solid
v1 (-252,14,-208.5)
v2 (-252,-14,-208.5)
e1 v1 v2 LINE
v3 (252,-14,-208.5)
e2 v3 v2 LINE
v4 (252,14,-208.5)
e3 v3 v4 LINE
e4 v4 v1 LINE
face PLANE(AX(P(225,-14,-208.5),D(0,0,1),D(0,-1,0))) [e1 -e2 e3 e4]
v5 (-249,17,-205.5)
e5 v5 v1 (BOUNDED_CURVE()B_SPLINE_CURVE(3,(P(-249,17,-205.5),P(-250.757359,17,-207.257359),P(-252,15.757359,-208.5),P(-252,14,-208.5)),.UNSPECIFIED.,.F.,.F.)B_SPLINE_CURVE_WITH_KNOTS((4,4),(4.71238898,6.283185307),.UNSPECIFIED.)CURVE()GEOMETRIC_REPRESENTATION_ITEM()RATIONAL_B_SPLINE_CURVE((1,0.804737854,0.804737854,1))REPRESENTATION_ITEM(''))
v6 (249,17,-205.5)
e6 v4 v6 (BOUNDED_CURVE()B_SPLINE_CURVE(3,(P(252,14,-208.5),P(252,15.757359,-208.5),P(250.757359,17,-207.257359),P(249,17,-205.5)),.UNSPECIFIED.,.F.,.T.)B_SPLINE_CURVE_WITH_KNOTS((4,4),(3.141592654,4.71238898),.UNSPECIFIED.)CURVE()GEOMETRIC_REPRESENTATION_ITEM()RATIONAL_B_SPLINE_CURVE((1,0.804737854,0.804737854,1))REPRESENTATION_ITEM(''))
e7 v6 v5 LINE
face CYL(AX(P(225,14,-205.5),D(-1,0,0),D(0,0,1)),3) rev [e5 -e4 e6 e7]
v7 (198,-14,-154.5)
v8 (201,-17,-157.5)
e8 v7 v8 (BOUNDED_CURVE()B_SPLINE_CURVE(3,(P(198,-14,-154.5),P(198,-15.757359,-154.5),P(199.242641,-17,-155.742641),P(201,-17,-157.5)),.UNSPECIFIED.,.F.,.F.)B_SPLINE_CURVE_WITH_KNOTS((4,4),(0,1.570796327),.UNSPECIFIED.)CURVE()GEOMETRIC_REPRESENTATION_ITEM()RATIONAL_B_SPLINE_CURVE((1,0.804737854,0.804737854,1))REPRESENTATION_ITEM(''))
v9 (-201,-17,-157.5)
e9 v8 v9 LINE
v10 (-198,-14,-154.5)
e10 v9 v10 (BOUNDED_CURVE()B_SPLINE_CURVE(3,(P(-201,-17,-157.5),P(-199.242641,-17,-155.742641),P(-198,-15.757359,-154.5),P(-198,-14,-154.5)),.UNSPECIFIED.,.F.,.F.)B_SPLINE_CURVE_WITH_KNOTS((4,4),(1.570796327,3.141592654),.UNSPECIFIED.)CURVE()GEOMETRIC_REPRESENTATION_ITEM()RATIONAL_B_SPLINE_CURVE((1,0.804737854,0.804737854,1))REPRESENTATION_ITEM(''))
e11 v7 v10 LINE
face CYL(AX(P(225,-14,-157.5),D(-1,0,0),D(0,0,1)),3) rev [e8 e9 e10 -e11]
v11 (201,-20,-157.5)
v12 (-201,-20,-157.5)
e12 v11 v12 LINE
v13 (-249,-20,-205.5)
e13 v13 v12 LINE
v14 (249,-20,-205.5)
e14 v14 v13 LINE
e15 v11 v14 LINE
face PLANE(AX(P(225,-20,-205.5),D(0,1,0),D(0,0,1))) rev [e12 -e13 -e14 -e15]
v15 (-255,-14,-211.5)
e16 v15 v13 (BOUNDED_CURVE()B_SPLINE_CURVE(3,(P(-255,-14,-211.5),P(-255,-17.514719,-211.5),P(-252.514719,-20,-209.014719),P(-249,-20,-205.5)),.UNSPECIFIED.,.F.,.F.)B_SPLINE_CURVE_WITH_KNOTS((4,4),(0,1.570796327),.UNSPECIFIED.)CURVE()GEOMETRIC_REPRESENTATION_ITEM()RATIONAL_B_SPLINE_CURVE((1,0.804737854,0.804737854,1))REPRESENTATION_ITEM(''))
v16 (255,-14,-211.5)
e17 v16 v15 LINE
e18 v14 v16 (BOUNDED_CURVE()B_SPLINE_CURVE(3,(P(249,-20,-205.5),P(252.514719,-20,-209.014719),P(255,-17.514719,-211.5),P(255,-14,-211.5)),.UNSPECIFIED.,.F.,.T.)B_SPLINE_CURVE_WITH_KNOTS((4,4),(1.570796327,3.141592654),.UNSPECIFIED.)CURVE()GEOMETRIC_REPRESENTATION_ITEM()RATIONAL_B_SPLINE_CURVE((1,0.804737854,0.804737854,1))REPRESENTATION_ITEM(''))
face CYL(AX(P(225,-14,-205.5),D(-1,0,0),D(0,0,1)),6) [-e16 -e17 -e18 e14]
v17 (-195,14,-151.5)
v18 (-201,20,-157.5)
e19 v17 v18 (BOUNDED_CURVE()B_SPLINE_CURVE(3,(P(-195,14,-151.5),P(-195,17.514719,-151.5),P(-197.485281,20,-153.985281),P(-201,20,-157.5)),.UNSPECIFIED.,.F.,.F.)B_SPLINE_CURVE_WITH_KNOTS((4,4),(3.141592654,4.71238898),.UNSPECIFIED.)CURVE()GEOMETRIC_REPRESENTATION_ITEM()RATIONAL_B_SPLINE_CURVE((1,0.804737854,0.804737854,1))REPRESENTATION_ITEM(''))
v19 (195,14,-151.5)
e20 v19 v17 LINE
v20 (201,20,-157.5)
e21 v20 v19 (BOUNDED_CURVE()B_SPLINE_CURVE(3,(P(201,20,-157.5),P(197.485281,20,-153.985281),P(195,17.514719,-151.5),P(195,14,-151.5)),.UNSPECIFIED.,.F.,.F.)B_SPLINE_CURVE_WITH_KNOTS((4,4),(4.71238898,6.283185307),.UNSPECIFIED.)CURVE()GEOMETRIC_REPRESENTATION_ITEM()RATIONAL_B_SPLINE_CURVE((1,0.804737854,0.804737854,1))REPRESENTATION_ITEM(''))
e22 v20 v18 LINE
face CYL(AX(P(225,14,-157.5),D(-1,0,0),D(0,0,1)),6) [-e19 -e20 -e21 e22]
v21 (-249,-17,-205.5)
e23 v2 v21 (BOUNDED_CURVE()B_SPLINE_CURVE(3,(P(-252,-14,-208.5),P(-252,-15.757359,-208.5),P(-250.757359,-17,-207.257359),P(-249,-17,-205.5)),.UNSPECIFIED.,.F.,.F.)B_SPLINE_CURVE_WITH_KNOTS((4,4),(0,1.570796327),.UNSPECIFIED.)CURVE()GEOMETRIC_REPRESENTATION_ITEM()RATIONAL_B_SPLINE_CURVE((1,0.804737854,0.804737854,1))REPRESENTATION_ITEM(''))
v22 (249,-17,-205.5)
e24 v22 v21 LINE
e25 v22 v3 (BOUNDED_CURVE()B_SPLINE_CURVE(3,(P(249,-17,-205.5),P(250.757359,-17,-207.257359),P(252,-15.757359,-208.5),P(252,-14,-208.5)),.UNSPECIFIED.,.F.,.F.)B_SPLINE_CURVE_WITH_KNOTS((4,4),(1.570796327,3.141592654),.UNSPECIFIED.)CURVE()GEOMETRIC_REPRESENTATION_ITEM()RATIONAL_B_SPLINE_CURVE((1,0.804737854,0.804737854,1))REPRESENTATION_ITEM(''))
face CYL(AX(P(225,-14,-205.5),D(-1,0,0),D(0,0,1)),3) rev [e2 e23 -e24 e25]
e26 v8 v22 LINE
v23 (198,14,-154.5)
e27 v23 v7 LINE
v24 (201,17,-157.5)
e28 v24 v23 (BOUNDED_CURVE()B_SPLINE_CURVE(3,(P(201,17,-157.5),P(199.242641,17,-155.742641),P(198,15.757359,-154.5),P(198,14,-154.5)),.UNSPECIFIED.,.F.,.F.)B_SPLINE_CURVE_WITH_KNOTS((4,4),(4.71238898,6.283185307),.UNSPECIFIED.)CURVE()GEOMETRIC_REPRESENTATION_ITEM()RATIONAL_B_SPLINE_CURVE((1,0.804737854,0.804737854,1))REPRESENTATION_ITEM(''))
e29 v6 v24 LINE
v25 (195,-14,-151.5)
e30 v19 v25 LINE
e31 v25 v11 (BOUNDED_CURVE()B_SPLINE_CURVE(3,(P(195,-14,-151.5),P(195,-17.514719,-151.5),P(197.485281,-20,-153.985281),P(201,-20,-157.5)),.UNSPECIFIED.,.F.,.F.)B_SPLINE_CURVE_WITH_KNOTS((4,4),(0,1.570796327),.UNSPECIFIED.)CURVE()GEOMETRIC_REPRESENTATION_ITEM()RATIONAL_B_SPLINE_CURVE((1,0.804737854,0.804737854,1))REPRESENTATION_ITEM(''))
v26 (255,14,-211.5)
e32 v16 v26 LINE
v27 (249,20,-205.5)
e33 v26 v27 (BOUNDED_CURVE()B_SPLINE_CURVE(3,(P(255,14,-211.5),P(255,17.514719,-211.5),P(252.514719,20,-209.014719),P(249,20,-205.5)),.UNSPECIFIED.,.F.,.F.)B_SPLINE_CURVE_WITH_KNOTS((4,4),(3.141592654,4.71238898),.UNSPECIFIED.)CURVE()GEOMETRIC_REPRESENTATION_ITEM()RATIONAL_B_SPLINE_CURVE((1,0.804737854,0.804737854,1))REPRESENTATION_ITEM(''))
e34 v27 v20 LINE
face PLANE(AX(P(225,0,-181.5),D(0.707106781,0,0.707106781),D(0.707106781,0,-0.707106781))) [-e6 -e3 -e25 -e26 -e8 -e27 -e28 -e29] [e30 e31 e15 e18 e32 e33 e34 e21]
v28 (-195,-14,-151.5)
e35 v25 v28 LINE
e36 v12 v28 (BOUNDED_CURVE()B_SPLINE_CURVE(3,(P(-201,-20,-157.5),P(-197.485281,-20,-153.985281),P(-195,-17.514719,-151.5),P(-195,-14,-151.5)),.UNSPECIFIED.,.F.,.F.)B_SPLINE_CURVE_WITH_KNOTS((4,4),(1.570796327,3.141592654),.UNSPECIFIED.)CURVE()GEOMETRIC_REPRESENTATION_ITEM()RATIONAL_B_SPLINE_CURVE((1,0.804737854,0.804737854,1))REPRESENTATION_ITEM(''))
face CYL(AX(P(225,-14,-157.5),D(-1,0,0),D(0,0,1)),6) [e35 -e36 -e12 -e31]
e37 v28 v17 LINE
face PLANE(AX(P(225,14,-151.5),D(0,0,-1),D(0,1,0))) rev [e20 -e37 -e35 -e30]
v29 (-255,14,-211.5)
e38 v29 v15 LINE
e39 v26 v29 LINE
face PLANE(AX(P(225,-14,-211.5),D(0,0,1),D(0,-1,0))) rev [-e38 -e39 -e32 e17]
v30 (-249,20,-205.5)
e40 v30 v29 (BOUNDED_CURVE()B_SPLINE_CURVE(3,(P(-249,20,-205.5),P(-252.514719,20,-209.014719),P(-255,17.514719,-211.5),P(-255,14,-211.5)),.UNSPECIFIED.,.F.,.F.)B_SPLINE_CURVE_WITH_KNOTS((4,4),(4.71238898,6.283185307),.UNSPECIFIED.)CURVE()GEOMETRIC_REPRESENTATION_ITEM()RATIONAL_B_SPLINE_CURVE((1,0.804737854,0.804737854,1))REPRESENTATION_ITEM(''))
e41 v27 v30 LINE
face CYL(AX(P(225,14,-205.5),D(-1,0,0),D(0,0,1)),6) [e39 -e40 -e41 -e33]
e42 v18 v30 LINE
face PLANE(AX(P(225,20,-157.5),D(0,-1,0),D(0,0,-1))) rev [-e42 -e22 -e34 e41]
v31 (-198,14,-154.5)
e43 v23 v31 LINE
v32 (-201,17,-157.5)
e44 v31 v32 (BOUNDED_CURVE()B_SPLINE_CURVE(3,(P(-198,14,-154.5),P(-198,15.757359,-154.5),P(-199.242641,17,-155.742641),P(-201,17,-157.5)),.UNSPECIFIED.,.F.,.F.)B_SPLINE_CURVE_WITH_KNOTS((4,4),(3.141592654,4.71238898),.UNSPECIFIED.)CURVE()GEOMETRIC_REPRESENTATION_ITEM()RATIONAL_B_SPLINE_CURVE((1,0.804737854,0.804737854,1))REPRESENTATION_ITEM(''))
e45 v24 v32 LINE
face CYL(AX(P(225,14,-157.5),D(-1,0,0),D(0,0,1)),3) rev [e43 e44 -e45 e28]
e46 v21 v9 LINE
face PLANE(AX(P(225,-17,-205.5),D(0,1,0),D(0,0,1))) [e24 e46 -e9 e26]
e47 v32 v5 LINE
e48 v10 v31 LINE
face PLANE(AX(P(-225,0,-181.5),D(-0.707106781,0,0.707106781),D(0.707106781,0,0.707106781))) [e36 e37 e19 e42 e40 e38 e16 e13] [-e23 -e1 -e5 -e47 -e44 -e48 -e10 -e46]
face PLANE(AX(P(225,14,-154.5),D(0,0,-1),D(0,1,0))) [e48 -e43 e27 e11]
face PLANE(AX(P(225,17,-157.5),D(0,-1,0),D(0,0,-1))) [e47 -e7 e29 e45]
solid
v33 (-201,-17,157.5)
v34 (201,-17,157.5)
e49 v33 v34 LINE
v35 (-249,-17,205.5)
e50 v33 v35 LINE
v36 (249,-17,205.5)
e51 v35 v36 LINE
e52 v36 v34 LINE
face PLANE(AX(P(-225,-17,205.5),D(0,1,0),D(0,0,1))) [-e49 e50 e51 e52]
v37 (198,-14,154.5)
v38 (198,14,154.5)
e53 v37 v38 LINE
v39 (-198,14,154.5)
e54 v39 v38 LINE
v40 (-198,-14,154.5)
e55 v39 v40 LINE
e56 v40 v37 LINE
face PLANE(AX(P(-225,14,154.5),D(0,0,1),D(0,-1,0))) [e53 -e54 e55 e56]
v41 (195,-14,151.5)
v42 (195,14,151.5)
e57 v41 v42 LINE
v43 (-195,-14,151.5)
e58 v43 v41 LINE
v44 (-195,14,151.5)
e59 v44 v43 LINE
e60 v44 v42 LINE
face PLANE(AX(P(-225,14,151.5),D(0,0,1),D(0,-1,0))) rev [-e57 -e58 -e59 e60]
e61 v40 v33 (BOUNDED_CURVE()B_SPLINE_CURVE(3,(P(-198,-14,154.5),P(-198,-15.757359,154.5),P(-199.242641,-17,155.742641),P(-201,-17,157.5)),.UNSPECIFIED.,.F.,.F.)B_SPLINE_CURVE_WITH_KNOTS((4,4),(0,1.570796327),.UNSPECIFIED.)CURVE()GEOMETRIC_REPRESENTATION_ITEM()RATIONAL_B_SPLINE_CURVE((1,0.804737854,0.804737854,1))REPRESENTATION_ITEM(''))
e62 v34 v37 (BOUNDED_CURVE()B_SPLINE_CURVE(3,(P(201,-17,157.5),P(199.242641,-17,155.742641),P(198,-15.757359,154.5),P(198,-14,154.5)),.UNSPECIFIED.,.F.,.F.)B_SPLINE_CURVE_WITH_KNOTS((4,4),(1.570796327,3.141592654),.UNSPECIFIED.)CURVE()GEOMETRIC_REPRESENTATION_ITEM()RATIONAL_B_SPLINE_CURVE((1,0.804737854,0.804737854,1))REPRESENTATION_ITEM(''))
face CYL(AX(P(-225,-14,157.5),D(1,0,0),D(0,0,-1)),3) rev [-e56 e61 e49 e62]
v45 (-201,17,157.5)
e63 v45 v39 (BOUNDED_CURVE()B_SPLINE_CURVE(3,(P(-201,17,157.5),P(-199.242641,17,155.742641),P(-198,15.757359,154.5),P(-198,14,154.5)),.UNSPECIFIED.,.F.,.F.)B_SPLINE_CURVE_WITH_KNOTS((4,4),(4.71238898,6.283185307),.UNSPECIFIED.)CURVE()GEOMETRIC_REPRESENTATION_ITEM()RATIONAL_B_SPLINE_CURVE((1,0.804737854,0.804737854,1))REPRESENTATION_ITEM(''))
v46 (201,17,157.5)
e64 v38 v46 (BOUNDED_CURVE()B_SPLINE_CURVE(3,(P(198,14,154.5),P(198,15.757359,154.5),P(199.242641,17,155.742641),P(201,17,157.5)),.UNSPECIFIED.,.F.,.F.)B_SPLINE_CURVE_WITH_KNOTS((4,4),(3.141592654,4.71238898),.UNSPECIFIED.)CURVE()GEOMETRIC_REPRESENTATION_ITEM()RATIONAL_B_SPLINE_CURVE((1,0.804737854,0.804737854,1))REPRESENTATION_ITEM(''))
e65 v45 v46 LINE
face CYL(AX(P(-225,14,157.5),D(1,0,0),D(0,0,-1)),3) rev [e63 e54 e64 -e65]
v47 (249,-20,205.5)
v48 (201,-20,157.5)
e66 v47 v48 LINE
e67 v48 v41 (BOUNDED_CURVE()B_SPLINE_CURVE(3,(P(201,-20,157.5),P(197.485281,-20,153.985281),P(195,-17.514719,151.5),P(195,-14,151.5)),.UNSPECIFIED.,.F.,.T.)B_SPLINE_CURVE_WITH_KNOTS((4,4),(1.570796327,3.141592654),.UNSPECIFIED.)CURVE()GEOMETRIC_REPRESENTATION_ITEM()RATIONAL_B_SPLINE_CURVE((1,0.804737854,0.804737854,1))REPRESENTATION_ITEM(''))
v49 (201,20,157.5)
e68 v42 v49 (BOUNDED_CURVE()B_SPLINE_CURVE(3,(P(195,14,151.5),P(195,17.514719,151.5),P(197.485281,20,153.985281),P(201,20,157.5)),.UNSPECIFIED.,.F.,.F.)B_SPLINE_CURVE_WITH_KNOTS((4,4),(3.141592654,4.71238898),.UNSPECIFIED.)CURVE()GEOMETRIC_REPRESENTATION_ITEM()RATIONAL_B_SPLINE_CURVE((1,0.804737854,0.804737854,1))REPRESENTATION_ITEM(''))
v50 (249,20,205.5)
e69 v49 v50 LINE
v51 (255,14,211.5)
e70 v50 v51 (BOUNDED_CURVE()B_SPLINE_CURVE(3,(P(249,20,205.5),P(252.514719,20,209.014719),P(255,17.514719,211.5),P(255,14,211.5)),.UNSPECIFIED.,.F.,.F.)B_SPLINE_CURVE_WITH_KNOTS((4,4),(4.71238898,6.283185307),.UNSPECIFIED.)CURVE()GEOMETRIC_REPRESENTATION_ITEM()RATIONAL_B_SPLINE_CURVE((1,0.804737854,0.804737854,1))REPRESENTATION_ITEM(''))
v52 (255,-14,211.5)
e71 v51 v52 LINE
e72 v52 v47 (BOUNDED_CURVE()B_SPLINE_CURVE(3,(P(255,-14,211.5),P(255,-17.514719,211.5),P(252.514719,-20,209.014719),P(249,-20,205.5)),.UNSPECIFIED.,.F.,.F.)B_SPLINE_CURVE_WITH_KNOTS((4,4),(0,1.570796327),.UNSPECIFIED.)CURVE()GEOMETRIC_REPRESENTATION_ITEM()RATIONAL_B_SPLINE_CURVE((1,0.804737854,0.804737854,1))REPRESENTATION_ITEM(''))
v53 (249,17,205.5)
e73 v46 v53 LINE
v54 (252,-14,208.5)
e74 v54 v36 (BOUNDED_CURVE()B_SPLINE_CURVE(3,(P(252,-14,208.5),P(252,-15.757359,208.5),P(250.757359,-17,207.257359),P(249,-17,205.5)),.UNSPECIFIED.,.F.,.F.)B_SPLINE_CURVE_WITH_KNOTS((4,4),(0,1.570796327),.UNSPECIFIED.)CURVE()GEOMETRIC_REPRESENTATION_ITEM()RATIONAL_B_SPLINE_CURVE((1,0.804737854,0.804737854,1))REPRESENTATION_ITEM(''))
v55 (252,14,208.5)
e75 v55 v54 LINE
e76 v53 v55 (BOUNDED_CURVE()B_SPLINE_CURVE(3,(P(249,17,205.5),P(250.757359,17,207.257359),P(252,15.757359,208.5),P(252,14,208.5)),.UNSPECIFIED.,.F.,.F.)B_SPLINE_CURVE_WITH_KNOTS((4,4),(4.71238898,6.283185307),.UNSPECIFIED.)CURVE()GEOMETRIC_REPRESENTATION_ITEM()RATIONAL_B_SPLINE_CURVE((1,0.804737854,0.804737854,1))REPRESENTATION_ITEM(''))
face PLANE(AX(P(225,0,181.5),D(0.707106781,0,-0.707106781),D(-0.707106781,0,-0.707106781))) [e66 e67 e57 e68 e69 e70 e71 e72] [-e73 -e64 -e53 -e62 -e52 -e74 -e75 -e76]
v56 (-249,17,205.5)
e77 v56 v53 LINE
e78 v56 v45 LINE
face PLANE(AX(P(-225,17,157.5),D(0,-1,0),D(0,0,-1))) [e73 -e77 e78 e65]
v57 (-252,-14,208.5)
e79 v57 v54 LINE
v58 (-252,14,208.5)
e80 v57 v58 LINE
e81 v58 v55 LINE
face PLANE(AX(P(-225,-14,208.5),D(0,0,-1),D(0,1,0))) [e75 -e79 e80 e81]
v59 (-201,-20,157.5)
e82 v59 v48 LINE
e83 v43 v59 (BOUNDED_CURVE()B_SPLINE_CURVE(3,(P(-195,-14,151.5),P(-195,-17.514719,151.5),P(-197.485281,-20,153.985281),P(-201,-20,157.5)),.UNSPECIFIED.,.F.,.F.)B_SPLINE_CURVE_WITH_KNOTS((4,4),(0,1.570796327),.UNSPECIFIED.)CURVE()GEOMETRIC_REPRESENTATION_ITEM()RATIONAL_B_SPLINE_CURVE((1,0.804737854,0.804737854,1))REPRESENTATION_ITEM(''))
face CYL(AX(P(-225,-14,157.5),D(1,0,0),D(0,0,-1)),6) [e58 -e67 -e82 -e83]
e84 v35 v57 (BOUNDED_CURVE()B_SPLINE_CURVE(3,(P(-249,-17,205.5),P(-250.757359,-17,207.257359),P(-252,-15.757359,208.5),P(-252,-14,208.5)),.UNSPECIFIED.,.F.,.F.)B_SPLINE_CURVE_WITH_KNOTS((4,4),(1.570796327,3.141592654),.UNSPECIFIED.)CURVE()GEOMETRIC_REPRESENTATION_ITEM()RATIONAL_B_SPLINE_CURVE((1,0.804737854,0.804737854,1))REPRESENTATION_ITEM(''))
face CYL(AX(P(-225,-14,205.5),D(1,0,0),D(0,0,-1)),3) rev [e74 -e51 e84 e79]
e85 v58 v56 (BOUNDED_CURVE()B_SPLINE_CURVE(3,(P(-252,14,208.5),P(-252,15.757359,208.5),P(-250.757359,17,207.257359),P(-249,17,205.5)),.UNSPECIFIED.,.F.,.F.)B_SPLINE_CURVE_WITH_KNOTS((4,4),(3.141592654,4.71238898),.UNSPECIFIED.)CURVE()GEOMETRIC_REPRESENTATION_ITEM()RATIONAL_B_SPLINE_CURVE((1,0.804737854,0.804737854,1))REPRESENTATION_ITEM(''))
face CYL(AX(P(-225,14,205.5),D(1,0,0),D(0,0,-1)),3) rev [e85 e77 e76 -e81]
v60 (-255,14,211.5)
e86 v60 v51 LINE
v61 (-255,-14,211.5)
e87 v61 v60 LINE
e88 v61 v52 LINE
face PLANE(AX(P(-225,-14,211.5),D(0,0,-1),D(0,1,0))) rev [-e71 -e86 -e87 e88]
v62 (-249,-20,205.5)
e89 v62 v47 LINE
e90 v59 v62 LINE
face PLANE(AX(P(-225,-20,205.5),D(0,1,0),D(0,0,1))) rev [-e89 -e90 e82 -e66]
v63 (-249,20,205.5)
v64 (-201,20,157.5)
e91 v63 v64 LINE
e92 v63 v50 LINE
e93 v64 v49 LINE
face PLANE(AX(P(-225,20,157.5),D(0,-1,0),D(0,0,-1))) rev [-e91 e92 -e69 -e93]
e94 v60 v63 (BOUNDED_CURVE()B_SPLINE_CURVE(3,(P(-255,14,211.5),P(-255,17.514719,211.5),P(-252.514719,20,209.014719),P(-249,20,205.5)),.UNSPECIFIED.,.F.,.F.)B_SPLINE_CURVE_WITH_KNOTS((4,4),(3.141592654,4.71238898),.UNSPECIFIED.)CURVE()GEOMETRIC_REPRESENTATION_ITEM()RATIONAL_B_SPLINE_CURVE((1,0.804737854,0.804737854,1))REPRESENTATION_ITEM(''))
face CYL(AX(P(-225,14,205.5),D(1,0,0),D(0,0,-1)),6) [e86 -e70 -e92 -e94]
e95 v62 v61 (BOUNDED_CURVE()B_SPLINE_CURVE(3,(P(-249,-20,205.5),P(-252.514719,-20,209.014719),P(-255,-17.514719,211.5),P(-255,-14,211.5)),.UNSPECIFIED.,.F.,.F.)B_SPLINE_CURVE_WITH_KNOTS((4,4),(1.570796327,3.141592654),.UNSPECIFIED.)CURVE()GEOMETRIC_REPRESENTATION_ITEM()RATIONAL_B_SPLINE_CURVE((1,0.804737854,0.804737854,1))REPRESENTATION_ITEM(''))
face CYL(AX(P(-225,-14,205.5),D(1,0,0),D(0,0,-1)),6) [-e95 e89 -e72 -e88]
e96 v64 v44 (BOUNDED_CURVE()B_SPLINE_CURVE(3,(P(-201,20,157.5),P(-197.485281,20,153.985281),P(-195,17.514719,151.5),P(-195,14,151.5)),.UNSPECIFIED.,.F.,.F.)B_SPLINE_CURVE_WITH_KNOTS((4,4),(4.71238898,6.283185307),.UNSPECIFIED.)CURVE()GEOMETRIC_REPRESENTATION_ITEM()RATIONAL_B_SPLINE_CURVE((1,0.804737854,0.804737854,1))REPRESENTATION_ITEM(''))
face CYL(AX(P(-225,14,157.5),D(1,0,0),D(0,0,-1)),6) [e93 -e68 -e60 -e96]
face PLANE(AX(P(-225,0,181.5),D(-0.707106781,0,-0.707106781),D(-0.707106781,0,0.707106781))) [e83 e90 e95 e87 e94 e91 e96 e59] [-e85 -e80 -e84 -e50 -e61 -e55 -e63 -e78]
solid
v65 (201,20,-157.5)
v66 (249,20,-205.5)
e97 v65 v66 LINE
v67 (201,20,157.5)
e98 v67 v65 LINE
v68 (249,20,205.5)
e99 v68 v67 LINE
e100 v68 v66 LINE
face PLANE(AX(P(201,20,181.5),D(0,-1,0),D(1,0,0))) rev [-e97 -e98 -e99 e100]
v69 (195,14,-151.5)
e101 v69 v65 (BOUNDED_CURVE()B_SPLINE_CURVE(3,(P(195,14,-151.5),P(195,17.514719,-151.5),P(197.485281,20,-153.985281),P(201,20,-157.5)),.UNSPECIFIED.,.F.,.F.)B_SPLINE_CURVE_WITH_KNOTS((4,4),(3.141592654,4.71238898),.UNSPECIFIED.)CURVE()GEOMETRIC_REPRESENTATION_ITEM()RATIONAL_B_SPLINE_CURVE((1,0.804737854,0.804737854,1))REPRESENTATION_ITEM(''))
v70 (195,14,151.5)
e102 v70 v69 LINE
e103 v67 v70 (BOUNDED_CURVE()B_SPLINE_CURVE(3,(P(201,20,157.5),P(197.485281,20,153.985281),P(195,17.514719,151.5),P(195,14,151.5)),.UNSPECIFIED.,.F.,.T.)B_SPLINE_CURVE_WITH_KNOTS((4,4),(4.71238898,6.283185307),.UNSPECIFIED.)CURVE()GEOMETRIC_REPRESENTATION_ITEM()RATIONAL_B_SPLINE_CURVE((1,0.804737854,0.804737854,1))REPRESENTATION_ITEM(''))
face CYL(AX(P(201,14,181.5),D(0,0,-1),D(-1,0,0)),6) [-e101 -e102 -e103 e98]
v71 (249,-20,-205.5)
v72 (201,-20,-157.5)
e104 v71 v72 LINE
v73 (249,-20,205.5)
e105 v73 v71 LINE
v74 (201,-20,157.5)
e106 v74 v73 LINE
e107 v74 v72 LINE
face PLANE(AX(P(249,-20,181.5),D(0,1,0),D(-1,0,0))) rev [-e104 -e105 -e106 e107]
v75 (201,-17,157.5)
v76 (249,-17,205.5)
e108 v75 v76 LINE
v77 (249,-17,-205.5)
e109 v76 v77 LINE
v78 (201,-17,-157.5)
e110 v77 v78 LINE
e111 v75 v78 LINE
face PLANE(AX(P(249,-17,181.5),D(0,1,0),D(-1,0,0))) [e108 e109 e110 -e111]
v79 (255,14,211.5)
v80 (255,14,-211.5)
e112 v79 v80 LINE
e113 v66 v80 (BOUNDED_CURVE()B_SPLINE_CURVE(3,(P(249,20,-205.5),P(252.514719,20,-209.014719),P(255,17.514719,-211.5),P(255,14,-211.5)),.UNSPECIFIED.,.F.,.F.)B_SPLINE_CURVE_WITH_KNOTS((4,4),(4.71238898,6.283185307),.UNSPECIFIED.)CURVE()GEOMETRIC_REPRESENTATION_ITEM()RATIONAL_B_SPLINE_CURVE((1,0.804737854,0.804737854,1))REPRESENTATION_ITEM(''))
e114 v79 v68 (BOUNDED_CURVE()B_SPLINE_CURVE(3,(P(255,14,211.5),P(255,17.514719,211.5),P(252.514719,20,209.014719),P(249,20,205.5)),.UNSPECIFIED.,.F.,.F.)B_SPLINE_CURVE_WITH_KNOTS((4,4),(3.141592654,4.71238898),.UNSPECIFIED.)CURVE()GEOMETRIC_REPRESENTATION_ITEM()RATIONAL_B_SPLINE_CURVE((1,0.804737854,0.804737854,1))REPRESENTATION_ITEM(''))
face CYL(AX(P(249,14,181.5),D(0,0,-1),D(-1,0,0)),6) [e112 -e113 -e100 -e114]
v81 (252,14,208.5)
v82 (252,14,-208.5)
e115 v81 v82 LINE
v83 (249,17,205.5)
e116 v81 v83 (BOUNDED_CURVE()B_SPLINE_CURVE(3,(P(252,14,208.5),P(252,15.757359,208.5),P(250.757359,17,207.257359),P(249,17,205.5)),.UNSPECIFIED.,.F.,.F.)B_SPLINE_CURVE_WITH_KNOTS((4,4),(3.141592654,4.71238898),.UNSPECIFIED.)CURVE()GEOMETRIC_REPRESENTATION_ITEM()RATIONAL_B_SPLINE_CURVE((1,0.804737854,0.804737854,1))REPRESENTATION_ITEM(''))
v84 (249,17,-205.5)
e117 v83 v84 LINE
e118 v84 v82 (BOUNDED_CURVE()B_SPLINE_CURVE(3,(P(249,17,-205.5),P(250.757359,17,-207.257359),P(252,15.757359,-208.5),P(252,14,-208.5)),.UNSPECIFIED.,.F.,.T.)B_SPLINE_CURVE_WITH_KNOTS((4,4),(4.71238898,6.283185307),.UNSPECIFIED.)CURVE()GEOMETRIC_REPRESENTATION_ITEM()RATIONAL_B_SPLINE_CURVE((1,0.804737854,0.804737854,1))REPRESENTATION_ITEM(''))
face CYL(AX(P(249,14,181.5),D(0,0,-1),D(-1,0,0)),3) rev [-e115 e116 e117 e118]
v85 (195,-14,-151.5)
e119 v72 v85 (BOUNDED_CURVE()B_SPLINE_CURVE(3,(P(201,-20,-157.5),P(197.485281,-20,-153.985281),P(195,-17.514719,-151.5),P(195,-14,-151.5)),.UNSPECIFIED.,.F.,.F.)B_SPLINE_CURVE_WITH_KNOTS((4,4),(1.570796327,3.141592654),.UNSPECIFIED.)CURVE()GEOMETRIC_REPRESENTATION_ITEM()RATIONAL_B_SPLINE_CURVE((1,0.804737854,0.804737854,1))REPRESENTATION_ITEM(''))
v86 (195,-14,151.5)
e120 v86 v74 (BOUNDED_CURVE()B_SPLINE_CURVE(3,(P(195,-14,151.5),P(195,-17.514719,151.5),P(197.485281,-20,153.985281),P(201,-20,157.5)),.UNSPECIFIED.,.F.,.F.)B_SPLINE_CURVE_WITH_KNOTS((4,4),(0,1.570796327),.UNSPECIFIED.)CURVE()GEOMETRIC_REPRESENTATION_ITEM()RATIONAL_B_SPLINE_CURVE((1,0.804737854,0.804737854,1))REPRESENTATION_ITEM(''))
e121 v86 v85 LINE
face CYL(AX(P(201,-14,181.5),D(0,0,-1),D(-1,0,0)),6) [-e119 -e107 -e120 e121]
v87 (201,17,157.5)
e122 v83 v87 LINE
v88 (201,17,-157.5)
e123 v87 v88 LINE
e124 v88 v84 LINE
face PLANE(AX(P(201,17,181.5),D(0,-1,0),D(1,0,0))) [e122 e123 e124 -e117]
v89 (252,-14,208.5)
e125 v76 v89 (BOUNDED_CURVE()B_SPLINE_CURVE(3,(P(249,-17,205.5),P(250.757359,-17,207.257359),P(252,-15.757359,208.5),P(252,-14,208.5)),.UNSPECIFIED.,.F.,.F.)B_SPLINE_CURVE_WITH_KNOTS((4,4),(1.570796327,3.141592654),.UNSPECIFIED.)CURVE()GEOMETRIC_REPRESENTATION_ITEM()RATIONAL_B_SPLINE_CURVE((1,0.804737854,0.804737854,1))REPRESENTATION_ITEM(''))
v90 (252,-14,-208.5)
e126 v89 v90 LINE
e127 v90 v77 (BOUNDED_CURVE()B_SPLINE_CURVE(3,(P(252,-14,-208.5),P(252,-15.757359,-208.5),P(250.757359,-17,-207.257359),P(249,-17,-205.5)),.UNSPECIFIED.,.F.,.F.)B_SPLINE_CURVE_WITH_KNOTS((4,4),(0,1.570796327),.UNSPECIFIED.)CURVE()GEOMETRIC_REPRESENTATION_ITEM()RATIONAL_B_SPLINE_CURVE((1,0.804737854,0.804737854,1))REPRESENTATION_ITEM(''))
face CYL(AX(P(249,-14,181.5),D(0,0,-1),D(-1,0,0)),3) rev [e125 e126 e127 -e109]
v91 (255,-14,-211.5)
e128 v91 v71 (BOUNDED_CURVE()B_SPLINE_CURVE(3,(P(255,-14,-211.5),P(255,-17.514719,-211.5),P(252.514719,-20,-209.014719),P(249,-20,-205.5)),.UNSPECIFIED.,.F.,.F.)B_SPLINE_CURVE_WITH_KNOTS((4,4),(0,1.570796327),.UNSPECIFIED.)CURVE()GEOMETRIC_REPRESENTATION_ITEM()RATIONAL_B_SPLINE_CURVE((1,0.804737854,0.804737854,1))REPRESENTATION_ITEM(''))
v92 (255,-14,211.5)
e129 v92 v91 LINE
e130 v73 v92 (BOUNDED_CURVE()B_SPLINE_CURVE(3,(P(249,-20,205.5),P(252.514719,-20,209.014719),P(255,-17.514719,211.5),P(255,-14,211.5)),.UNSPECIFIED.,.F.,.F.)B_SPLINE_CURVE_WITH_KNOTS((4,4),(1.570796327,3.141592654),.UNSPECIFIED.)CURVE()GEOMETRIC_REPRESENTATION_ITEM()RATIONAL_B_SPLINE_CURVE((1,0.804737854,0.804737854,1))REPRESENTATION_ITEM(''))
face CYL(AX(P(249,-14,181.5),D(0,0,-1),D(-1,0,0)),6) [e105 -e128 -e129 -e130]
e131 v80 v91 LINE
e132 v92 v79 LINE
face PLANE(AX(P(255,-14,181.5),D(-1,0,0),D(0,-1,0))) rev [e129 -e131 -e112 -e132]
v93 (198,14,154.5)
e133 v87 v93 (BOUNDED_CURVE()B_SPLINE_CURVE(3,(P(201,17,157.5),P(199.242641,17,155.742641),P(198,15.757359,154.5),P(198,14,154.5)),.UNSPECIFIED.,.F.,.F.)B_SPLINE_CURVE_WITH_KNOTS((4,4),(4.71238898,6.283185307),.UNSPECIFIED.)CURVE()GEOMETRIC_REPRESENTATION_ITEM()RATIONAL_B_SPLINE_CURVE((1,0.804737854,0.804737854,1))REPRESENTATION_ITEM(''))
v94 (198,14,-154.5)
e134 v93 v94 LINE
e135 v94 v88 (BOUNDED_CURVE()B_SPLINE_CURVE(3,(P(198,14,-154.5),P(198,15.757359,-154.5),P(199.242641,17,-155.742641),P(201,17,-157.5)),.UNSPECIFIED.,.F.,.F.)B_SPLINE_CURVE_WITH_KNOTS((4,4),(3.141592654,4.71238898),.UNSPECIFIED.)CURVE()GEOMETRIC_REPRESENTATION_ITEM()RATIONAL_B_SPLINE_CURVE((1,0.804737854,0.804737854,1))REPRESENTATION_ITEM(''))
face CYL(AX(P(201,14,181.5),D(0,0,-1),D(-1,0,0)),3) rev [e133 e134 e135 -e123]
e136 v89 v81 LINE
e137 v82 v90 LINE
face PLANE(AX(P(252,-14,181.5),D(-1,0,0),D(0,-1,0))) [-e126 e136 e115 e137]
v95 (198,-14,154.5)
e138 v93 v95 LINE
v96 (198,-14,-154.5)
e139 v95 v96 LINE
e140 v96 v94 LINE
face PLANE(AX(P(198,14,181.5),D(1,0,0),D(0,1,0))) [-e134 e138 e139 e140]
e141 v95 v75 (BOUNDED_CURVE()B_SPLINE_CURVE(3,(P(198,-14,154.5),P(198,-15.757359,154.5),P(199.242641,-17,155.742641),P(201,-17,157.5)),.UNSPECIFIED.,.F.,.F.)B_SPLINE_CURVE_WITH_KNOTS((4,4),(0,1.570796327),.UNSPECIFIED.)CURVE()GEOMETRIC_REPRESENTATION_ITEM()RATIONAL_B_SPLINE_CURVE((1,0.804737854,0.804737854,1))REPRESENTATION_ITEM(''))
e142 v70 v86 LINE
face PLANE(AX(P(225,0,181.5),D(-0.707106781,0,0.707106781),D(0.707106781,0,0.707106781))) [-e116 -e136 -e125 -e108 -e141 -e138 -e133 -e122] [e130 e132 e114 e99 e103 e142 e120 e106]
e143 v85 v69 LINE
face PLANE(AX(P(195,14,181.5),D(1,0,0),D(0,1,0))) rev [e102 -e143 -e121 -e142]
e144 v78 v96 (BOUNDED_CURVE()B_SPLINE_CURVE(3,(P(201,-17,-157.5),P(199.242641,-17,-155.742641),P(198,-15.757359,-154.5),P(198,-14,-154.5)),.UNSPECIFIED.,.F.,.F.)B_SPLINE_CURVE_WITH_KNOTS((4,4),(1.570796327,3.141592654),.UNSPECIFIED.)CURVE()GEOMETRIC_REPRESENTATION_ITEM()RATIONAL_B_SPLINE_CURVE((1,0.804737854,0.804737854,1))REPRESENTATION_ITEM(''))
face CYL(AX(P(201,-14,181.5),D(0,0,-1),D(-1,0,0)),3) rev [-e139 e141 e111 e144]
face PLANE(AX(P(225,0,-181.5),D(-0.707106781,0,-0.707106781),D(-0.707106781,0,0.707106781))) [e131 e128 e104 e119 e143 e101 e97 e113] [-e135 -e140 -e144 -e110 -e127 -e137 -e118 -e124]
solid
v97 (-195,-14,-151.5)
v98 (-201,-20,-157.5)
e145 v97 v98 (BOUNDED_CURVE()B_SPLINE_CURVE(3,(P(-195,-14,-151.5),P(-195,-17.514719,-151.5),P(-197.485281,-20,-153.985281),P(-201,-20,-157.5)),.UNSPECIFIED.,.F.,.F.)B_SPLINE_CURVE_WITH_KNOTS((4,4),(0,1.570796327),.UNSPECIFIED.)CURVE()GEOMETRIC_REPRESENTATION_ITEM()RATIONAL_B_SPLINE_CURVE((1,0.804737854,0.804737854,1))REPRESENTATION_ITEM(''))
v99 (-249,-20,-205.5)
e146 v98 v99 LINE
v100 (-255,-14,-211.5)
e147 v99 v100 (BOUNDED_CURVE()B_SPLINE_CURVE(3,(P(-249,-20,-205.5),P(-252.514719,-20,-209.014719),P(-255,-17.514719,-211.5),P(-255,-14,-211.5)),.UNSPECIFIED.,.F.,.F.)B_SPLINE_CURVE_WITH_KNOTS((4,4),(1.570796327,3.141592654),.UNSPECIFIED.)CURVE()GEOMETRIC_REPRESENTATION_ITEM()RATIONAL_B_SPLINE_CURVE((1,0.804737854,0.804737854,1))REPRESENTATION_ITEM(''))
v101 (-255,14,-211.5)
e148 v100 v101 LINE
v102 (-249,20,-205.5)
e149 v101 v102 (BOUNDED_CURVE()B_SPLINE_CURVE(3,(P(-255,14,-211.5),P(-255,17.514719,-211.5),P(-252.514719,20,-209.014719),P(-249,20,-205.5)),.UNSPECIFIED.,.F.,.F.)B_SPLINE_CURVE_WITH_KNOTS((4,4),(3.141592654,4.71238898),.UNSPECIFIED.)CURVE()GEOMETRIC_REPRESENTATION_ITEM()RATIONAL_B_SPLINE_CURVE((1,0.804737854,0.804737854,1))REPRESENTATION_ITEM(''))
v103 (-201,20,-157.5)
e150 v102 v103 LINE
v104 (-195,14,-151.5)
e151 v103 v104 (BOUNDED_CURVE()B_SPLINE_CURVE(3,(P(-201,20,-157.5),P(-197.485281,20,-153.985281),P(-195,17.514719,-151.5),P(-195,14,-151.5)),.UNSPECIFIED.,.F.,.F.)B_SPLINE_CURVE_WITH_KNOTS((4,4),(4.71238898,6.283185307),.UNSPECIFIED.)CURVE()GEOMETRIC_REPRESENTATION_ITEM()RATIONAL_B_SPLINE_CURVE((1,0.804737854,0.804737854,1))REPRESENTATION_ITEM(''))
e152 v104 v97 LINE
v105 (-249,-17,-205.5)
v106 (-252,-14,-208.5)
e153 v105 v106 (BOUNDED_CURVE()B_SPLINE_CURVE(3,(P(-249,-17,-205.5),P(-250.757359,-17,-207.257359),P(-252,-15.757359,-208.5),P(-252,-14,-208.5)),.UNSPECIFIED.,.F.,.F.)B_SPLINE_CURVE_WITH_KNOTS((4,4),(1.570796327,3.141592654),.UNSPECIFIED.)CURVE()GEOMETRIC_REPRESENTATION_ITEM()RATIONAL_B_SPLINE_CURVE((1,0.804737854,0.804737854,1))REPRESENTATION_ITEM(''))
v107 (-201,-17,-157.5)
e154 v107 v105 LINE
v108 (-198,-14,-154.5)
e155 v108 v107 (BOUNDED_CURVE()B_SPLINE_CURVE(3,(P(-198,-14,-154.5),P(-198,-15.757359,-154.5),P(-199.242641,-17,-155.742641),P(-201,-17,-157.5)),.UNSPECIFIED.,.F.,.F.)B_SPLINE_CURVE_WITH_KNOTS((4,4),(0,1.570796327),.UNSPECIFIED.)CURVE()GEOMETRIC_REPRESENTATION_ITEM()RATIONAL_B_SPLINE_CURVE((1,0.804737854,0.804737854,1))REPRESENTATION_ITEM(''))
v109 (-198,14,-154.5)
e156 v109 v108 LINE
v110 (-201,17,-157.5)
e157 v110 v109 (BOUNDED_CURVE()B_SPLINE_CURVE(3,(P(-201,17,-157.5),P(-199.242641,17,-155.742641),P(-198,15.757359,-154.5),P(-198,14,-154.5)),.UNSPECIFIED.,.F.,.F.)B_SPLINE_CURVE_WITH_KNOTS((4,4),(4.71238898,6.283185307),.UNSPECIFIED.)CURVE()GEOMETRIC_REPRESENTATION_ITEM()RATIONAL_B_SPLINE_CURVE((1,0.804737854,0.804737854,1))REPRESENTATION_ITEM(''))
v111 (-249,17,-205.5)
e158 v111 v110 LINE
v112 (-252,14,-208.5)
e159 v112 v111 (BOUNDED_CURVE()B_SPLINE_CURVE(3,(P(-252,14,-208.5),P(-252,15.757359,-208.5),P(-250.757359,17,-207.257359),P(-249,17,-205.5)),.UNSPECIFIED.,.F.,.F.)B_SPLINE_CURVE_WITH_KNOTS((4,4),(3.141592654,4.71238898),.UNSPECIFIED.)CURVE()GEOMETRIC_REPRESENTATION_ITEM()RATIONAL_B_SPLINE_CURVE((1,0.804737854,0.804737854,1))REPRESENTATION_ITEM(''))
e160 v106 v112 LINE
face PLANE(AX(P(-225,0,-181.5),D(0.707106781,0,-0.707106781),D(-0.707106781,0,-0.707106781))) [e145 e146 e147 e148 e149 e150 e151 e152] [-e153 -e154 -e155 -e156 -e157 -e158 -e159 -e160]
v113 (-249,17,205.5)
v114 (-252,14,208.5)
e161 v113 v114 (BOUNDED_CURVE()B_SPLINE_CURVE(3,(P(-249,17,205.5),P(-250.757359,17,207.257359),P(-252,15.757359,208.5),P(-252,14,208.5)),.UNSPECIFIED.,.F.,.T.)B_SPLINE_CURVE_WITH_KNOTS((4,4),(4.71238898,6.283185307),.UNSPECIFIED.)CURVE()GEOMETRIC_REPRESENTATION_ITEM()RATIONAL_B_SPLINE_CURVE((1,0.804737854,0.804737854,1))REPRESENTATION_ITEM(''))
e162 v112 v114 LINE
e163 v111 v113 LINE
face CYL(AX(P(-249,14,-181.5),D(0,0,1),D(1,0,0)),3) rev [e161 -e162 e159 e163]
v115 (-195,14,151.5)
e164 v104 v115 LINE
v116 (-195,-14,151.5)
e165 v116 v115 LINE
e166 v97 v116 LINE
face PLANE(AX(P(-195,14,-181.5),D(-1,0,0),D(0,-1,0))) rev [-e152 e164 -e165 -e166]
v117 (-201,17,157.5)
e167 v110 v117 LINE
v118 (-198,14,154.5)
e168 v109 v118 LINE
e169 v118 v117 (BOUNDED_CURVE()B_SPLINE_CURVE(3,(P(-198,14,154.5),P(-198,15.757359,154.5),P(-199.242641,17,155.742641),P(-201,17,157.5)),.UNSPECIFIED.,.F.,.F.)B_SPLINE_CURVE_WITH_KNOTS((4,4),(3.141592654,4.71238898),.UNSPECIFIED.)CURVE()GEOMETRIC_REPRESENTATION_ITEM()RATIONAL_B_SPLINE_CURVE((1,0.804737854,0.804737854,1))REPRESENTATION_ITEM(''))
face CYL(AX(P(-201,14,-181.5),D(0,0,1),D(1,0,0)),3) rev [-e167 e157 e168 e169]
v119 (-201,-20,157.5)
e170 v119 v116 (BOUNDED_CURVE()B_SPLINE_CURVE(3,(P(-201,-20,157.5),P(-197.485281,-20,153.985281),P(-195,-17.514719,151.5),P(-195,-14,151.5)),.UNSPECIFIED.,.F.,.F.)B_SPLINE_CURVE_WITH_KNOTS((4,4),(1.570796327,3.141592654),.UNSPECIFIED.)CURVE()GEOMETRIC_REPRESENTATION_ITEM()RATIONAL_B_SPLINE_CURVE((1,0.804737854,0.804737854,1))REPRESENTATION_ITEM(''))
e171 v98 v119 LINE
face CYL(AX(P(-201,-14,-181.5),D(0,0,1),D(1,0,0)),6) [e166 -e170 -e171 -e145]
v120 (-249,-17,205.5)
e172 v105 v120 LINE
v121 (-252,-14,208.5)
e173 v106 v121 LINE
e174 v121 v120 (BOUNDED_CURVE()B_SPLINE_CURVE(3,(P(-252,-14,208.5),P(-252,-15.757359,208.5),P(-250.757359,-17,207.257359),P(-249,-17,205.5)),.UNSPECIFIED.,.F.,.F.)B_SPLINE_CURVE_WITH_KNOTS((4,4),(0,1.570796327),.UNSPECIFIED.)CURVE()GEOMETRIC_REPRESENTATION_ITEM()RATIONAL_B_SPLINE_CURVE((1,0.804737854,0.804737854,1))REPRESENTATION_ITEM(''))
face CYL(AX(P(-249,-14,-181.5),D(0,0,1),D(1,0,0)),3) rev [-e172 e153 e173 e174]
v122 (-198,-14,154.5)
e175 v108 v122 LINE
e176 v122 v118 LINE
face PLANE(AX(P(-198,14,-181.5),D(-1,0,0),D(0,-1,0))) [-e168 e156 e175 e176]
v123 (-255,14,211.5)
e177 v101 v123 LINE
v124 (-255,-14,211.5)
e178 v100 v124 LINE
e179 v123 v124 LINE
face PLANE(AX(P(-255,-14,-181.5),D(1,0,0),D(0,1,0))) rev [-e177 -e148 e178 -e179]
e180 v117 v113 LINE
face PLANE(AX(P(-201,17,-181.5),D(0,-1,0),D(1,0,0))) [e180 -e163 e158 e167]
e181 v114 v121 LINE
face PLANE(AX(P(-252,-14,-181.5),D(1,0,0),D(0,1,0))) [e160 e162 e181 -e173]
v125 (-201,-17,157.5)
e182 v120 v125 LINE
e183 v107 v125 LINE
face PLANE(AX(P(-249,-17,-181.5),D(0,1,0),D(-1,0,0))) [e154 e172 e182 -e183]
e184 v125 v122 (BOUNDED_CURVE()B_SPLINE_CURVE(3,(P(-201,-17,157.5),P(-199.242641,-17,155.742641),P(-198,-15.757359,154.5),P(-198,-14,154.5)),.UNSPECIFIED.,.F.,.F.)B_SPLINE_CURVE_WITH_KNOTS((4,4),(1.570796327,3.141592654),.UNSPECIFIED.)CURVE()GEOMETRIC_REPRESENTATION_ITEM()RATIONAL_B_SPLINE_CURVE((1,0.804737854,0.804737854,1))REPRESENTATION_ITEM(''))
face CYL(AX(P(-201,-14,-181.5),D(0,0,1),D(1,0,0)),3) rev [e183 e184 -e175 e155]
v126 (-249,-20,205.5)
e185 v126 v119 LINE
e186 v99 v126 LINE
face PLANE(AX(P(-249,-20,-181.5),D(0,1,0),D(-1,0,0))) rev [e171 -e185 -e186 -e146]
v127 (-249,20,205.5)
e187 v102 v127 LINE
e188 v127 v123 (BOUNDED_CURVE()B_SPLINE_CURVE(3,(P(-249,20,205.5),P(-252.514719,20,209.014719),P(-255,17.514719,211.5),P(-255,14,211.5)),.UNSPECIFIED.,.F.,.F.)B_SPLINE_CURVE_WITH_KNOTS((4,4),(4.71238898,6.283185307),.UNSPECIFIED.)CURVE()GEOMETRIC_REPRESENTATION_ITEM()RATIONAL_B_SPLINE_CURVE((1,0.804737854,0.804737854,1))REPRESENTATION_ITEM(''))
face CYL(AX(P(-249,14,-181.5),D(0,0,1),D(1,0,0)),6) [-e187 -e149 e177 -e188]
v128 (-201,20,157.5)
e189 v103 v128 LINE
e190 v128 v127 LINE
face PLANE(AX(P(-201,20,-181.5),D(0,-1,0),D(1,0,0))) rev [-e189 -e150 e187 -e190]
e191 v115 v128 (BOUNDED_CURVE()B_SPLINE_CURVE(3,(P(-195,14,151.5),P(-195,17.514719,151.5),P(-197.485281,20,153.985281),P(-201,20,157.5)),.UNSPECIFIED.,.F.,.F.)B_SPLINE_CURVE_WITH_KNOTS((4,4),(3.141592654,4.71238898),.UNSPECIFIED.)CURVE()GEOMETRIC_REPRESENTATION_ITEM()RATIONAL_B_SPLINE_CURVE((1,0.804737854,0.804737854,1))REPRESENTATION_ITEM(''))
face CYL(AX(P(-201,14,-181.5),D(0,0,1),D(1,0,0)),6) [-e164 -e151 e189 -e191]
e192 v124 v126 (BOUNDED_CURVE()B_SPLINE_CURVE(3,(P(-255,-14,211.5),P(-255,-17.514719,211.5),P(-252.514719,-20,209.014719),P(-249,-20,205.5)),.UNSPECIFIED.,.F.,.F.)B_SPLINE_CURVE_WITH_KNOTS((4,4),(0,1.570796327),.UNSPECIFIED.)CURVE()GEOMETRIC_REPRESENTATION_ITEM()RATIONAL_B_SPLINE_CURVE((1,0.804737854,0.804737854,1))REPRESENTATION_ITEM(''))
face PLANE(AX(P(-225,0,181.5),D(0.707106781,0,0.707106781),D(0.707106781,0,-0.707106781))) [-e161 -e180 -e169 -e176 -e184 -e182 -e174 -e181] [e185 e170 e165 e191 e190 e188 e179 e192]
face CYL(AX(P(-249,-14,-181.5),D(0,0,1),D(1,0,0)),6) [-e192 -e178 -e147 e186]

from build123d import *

# Parameters (mm, degrees)
GB_T_6728_2002_RECTANGULAR_HOLLOW_SECTIO_DEPTH      = 400.055512755
GB_T_6728_2002_RECTANGULAR_HOLLOW_SECTIO_DEPTH_BACK = 37.055512755
GB_T_6728_2002_RECTANGULAR_HOLLOW_SE_4_DEPTH        = 524.111025509
GB_T_6728_2002_RECTANGULAR_HOLLOW_SE_6_DEPTH        = 437.111025509
GB_T_6728_2002_RECTANGULAR_HOLLOW_SE_8_DEPTH        = 524.111025509


with BuildPart() as part:
    # Sketch1 → GB/T 6728-2002 Rectangular Hollow Section 60X40X3(1) (new, two sides: drawn at the far end of the back side and taken through both)
    with BuildSketch(Plane(origin=(-225, 0, 181.5), x_dir=(0, 1, 0), z_dir=(0, 0, -1)).offset(-GB_T_6728_2002_RECTANGULAR_HOLLOW_SECTIO_DEPTH_BACK)):
        with BuildLine():
            Line((-14, -30), (14, -30))
            ThreePointArc((14, -30), (18.242640687, -28.242640687), (20, -24))
            Line((20, -24), (20, 24))
            ThreePointArc((20, 24), (18.242640687, 28.242640687), (14, 30))
            Line((14, 30), (-14, 30))
            ThreePointArc((-14, 30), (-18.242640687, 28.242640687), (-20, 24))
            Line((-20, 24), (-20, -24))
            ThreePointArc((-20, -24), (-18.242640687, -28.242640687), (-14, -30))
        make_face()
        with BuildLine():
            Line((-14, -27), (14, -27))
            ThreePointArc((14, -27), (16.121320344, -26.121320344), (17, -24))
            Line((17, -24), (17, 24))
            ThreePointArc((17, 24), (16.121320344, 26.121320344), (14, 27))
            Line((14, 27), (-14, 27))
            ThreePointArc((-14, 27), (-16.121320344, 26.121320344), (-17, 24))
            Line((-17, 24), (-17, -24))
            ThreePointArc((-17, -24), (-16.121320344, -26.121320344), (-14, -27))
        make_face(mode=Mode.SUBTRACT)
    extrude(amount=GB_T_6728_2002_RECTANGULAR_HOLLOW_SECTIO_DEPTH + GB_T_6728_2002_RECTANGULAR_HOLLOW_SECTIO_DEPTH_BACK)

    # GB_T 6728-2002 Rectangular Hollow Se 2
    split(bisect_by=Plane(origin=(-225, 0, 181.5), x_dir=(0, -1, 0), z_dir=(-0.707106781, 0, -0.707106781)), keep=Keep.TOP)

    # GB_T 6728-2002 Rectangular Hollow Se 3
    split(bisect_by=Plane(origin=(-225, 0, -181.5), x_dir=(0, -1, 0), z_dir=(-0.707106781, 0, 0.707106781)), keep=Keep.TOP)


with BuildPart() as body_2:
    # Sketch1 on segment 2 (carried to segment 2) → GB_T 6728-2002 Rectangular Hollow Se 4 (new body)
    with BuildSketch(Plane(origin=(-262.055512755, 0, -181.5), x_dir=(0, 1, 0), z_dir=(1, 0, 0))):
        with BuildLine():
            Line((-14, -30), (14, -30))
            ThreePointArc((14, -30), (18.242640687, -28.242640687), (20, -24))
            Line((20, -24), (20, 24))
            ThreePointArc((20, 24), (18.242640687, 28.242640687), (14, 30))
            Line((14, 30), (-14, 30))
            ThreePointArc((-14, 30), (-18.242640687, 28.242640687), (-20, 24))
            Line((-20, 24), (-20, -24))
            ThreePointArc((-20, -24), (-18.242640687, -28.242640687), (-14, -30))
        make_face()
        with BuildLine():
            Line((-14, -27), (14, -27))
            ThreePointArc((14, -27), (16.121320344, -26.121320344), (17, -24))
            Line((17, -24), (17, 24))
            ThreePointArc((17, 24), (16.121320344, 26.121320344), (14, 27))
            Line((14, 27), (-14, 27))
            ThreePointArc((-14, 27), (-16.121320344, 26.121320344), (-17, 24))
            Line((-17, 24), (-17, -24))
            ThreePointArc((-17, -24), (-16.121320344, -26.121320344), (-14, -27))
        make_face(mode=Mode.SUBTRACT)
    extrude(amount=GB_T_6728_2002_RECTANGULAR_HOLLOW_SE_4_DEPTH)

    # GB_T 6728-2002 Rectangular Hollow Se 4 m
    split(bisect_by=Plane(origin=(225, 0, -181.5), x_dir=(0, -1, 0), z_dir=(-0.707106781, 0, -0.707106781)), keep=Keep.TOP)

    # GB_T 6728-2002 Rectangular Hollow Se 5
    split(bisect_by=Plane(origin=(-225, 0, -181.5), x_dir=(0, 1, 0), z_dir=(0.707106781, 0, -0.707106781)), keep=Keep.TOP)


with BuildPart() as body_3:
    # Sketch1 on segment 3 (carried to segment 3) → GB_T 6728-2002 Rectangular Hollow Se 6 (new body)
    with BuildSketch(Plane(origin=(225, 0, -218.555512755), x_dir=(0, 1, 0), z_dir=(0, 0, 1))):
        with BuildLine():
            Line((-14, -30), (14, -30))
            ThreePointArc((14, -30), (18.242640687, -28.242640687), (20, -24))
            Line((20, -24), (20, 24))
            ThreePointArc((20, 24), (18.242640687, 28.242640687), (14, 30))
            Line((14, 30), (-14, 30))
            ThreePointArc((-14, 30), (-18.242640687, 28.242640687), (-20, 24))
            Line((-20, 24), (-20, -24))
            ThreePointArc((-20, -24), (-18.242640687, -28.242640687), (-14, -30))
        make_face()
        with BuildLine():
            Line((-14, -27), (14, -27))
            ThreePointArc((14, -27), (16.121320344, -26.121320344), (17, -24))
            Line((17, -24), (17, 24))
            ThreePointArc((17, 24), (16.121320344, 26.121320344), (14, 27))
            Line((14, 27), (-14, 27))
            ThreePointArc((-14, 27), (-16.121320344, 26.121320344), (-17, 24))
            Line((-17, 24), (-17, -24))
            ThreePointArc((-17, -24), (-16.121320344, -26.121320344), (-14, -27))
        make_face(mode=Mode.SUBTRACT)
    extrude(amount=GB_T_6728_2002_RECTANGULAR_HOLLOW_SE_6_DEPTH)

    # GB_T 6728-2002 Rectangular Hollow Se 6 m
    split(bisect_by=Plane(origin=(225, 0, 181.5), x_dir=(0, 1, 0), z_dir=(0.707106781, 0, -0.707106781)), keep=Keep.TOP)

    # GB_T 6728-2002 Rectangular Hollow Se 7
    split(bisect_by=Plane(origin=(225, 0, -181.5), x_dir=(0, 1, 0), z_dir=(0.707106781, 0, 0.707106781)), keep=Keep.TOP)


with BuildPart() as body_4:
    # Sketch1 on segment 4 (carried to segment 4) → GB_T 6728-2002 Rectangular Hollow Se 8 (new body)
    with BuildSketch(Plane(origin=(262.055512755, 0, 181.5), x_dir=(0, 1, 0), z_dir=(-1, 0, 0))):
        with BuildLine():
            Line((-14, -30), (14, -30))
            ThreePointArc((14, -30), (18.242640687, -28.242640687), (20, -24))
            Line((20, -24), (20, 24))
            ThreePointArc((20, 24), (18.242640687, 28.242640687), (14, 30))
            Line((14, 30), (-14, 30))
            ThreePointArc((-14, 30), (-18.242640687, 28.242640687), (-20, 24))
            Line((-20, 24), (-20, -24))
            ThreePointArc((-20, -24), (-18.242640687, -28.242640687), (-14, -30))
        make_face()
        with BuildLine():
            Line((-14, -27), (14, -27))
            ThreePointArc((14, -27), (16.121320344, -26.121320344), (17, -24))
            Line((17, -24), (17, 24))
            ThreePointArc((17, 24), (16.121320344, 26.121320344), (14, 27))
            Line((14, 27), (-14, 27))
            ThreePointArc((-14, 27), (-16.121320344, 26.121320344), (-17, 24))
            Line((-17, 24), (-17, -24))
            ThreePointArc((-17, -24), (-16.121320344, -26.121320344), (-14, -27))
        make_face(mode=Mode.SUBTRACT)
    extrude(amount=GB_T_6728_2002_RECTANGULAR_HOLLOW_SE_8_DEPTH)

    # GB_T 6728-2002 Rectangular Hollow Se 8 m
    split(bisect_by=Plane(origin=(225, 0, 181.5), x_dir=(0, -1, 0), z_dir=(-0.707106781, 0, 0.707106781)), keep=Keep.TOP)

    # GB_T 6728-2002 Rectangular Hollow Se 9
    split(bisect_by=Plane(origin=(-225, 0, 181.5), x_dir=(0, 1, 0), z_dir=(0.707106781, 0, 0.707106781)), keep=Keep.TOP)


solid = Compound([part.part, body_2.part, body_3.part, body_4.part])
